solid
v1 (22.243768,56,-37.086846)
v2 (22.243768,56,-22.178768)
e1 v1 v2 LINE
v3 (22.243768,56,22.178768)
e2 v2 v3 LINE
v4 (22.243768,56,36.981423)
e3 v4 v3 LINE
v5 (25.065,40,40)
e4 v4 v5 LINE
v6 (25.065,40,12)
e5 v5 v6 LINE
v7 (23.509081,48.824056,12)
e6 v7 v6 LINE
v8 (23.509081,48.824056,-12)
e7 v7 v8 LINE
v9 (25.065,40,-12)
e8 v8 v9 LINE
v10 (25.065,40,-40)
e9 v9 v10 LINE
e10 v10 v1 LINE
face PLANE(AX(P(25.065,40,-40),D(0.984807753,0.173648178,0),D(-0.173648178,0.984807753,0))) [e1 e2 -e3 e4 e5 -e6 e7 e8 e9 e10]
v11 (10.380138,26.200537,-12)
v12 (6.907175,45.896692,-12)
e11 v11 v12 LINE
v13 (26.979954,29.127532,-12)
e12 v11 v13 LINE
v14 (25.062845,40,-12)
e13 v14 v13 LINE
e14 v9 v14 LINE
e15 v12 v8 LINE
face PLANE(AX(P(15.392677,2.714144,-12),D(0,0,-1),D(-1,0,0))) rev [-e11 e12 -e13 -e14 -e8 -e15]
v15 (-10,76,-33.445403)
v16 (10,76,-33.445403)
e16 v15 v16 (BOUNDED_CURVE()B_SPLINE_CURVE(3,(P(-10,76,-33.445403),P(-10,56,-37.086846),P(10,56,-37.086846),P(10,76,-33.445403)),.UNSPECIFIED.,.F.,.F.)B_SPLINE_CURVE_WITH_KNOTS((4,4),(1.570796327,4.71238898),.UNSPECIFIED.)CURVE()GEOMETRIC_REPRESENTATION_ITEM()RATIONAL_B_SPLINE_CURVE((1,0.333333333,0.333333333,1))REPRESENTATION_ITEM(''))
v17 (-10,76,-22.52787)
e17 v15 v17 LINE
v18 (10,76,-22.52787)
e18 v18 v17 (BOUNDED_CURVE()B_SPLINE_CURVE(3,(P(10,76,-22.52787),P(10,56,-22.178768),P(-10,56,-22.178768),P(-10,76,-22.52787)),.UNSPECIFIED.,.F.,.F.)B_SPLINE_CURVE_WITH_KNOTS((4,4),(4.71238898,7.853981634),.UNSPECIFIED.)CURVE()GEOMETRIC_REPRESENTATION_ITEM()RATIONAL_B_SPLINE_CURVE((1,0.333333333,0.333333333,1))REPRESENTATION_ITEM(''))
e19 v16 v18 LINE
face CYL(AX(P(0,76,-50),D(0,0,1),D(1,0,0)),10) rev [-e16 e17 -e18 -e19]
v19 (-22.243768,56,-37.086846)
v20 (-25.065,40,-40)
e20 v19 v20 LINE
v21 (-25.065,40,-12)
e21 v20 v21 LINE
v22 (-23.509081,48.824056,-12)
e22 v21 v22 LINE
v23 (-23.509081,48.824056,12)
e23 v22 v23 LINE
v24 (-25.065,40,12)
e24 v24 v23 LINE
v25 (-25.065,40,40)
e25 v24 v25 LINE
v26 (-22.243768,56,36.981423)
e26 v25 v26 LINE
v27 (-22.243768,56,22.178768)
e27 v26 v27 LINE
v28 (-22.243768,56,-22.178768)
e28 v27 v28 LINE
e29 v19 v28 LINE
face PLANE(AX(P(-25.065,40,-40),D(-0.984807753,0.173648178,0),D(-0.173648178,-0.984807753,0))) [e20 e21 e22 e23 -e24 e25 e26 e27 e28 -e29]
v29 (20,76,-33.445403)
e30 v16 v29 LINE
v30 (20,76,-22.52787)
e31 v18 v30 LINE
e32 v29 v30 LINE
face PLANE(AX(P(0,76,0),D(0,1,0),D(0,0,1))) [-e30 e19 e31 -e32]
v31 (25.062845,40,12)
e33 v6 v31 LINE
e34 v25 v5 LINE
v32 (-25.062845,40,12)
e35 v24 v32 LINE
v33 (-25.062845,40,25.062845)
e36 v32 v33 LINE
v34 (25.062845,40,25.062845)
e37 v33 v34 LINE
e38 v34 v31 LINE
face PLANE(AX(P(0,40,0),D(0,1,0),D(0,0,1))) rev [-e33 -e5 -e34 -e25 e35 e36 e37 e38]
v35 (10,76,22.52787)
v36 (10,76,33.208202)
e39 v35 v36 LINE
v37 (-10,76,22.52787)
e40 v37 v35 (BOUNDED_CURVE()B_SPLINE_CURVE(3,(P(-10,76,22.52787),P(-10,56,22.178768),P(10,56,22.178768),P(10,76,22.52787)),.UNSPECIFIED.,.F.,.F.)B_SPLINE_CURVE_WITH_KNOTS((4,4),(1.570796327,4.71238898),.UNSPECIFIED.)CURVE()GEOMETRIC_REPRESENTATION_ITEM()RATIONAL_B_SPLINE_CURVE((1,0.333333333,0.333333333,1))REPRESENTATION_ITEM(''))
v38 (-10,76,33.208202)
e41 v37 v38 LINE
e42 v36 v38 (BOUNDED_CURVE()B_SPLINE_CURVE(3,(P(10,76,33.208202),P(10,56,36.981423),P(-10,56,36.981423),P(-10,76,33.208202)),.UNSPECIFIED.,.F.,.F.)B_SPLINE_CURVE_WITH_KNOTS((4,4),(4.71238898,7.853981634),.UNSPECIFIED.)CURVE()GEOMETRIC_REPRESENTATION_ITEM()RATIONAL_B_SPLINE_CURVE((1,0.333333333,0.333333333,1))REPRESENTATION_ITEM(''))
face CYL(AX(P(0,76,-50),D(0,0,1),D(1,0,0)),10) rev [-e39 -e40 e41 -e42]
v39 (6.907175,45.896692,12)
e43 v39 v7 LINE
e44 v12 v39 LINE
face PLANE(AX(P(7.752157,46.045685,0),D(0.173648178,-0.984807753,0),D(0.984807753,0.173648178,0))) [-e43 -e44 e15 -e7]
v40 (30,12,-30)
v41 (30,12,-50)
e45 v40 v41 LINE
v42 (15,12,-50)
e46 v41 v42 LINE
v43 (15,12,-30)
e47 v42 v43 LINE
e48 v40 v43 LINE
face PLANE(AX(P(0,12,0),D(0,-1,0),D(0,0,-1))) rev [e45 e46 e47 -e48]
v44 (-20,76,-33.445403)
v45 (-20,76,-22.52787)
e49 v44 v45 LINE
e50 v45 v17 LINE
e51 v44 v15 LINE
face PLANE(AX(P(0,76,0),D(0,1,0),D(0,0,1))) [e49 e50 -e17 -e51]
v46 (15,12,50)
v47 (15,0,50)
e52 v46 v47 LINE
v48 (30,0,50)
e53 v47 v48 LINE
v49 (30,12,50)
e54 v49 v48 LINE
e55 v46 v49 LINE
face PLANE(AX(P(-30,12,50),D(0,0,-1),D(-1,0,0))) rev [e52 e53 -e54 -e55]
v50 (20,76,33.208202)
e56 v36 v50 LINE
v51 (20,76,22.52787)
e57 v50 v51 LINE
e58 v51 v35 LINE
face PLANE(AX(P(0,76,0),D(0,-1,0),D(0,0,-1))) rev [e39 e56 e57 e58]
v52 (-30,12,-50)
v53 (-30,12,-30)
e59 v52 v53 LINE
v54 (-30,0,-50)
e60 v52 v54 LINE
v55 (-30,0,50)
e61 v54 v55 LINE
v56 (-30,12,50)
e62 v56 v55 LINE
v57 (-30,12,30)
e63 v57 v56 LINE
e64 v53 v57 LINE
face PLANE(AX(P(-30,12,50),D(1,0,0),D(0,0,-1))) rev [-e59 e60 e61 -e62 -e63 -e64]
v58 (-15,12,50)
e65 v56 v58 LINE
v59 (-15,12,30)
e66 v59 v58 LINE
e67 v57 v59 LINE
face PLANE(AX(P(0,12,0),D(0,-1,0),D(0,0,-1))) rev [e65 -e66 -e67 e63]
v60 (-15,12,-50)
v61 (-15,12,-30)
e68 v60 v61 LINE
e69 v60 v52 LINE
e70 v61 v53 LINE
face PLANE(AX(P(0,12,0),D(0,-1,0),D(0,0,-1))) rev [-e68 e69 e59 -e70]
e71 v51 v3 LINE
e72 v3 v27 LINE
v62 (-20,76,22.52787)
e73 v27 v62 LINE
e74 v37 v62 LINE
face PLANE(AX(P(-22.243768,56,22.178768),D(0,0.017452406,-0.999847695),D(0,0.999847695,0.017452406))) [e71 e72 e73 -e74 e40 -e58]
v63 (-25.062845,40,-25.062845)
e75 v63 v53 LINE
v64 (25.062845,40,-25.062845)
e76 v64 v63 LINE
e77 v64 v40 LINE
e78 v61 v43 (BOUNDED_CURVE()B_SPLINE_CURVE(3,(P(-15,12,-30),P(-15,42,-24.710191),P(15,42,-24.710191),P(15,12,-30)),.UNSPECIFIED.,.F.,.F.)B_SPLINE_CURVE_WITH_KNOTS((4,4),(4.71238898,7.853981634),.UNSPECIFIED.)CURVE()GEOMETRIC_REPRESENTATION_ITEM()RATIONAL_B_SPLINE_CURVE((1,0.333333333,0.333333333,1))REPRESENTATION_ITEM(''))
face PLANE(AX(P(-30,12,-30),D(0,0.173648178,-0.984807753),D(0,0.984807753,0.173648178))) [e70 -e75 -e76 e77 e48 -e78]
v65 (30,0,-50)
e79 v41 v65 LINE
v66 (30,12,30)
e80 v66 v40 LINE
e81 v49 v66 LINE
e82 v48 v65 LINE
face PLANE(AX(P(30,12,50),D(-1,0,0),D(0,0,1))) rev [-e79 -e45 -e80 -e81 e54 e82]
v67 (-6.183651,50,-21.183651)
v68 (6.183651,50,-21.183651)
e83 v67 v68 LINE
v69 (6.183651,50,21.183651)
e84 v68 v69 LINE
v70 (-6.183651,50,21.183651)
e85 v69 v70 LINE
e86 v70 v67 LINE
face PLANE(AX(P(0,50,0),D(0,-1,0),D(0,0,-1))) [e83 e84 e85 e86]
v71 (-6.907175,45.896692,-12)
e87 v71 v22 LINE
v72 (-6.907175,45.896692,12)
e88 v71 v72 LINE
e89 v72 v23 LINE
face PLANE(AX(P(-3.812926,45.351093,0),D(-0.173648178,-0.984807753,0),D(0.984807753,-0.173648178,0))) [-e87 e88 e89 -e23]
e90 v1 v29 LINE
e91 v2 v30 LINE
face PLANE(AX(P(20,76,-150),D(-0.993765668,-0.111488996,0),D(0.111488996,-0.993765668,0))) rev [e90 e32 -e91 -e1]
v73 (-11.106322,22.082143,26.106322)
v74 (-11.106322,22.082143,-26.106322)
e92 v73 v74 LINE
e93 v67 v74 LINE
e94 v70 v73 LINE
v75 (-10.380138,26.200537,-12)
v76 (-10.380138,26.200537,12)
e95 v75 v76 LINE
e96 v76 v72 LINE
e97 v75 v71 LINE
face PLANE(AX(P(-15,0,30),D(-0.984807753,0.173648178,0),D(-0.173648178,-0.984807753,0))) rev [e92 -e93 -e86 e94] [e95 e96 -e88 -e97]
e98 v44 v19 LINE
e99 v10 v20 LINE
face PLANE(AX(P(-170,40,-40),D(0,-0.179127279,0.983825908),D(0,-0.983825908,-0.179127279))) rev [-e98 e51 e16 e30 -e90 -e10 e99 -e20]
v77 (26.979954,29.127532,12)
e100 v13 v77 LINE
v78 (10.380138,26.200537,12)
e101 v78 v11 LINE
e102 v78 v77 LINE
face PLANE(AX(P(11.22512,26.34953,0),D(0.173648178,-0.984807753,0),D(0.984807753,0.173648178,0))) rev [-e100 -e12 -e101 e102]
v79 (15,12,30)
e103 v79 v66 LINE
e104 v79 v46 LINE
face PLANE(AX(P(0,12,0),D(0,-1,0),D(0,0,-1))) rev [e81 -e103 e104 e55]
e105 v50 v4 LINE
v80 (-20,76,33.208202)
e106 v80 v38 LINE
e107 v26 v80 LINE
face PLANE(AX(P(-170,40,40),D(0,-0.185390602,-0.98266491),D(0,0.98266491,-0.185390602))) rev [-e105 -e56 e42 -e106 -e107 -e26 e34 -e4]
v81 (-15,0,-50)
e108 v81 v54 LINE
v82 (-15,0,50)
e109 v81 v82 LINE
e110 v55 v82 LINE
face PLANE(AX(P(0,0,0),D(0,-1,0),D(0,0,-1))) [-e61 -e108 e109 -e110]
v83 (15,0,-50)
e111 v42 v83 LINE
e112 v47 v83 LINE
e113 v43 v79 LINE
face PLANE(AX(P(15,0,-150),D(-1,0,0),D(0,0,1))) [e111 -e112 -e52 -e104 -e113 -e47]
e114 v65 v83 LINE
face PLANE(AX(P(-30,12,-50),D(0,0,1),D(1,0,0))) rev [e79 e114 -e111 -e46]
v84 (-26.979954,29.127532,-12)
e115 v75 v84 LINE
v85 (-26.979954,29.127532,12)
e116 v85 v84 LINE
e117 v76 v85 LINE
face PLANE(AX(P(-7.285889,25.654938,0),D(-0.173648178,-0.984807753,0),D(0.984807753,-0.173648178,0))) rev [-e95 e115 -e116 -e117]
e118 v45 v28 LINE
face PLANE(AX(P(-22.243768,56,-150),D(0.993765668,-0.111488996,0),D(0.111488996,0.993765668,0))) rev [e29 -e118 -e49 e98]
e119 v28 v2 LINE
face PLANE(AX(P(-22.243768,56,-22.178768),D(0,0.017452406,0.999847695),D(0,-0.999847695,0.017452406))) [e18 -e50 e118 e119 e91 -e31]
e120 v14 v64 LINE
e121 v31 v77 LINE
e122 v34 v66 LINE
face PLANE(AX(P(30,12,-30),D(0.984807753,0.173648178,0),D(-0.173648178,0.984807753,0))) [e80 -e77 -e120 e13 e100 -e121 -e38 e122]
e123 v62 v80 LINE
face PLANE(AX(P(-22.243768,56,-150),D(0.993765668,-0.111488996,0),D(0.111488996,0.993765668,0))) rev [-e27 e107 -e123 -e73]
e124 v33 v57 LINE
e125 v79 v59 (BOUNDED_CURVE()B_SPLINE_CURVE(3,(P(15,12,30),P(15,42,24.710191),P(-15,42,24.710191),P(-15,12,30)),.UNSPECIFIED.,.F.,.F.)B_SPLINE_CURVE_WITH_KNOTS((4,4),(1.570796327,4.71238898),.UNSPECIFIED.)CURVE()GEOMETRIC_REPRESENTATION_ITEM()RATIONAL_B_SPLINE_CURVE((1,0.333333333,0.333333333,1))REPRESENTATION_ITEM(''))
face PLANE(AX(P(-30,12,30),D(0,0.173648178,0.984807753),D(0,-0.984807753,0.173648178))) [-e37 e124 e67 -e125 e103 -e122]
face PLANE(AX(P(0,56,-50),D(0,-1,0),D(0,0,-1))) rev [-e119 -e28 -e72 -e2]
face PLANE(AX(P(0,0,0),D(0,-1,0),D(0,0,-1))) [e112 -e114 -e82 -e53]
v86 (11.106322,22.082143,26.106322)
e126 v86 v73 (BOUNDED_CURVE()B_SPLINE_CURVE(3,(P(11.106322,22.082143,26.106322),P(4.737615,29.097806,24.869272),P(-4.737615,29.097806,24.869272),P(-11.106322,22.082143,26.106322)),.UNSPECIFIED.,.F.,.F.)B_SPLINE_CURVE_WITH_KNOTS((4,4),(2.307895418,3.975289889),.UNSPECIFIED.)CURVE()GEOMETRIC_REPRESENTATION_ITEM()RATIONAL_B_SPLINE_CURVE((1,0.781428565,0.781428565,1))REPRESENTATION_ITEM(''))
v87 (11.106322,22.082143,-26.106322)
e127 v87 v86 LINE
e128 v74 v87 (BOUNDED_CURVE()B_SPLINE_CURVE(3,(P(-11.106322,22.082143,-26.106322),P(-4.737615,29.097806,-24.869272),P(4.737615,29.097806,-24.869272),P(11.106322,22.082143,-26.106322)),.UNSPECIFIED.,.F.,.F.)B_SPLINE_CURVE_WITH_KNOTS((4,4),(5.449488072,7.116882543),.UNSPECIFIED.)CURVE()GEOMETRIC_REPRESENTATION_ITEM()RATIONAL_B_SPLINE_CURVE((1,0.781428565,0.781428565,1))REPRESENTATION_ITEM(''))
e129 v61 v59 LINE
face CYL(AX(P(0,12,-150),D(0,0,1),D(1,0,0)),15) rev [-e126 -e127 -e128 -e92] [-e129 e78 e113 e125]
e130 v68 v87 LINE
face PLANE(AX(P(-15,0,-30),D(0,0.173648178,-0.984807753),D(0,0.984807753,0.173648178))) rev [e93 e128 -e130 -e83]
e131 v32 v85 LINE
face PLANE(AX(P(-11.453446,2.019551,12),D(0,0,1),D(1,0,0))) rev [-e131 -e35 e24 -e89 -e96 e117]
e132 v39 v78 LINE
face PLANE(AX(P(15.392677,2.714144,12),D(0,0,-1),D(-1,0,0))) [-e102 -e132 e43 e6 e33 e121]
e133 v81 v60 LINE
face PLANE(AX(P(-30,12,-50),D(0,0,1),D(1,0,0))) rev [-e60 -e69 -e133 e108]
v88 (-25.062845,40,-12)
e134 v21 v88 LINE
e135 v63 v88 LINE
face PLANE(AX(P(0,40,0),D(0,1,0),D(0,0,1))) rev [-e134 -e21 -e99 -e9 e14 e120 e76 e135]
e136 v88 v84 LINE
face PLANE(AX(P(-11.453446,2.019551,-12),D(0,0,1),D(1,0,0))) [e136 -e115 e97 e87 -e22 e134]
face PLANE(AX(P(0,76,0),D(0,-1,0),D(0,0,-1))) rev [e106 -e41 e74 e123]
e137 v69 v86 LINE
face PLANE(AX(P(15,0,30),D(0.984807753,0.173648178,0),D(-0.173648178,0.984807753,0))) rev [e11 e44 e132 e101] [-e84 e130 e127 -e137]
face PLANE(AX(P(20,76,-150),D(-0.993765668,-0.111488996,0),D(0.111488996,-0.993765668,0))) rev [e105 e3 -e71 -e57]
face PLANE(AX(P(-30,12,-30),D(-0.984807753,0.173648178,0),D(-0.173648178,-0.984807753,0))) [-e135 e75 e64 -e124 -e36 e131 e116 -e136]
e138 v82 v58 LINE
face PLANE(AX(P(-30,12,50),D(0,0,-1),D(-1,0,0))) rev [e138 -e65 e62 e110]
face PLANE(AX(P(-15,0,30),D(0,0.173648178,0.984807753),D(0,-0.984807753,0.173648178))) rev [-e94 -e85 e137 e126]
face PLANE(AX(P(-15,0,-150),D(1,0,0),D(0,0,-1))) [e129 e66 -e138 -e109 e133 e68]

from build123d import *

# Parameters (mm, degrees)
BASE_PLATE_SKETCH_W            = 60
BASE_PLATE_SKETCH_H            = 100
BASE_PLATE_100X60X12_DEPTH     = 12
PEDESTAL_SKETCH_W              = 60
PEDESTAL_SKETCH_H              = 60
TAPERED_PEDESTAL_DEPTH         = 28
TAPERED_PEDESTAL_TAPER         = 10
FOOT_CHANNEL_SKETCH_W          = 30
FOOT_CHANNEL_SKETCH_H          = 12
FOOT_CHANNEL_CUT_DEPTH         = 200
UPPER_BLOCK_SKETCH_W           = 50.13
UPPER_BLOCK_SKETCH_H           = 80
UPPER_BLOCK_80X50_DEPTH        = 16
UPPER_BLOCK_80X50_TAPER        = 10
TOP_SLOT_SKETCH_W              = 24
TOP_SLOT_SKETCH_H              = 8.960181453
TOP_SLOT_CUT_DEPTH             = 16
PEDESTAL_RELIEF_SKETCH_W       = 30
PEDESTAL_RELIEF_SKETCH_H       = 60
PEDESTAL_RELIEF_CUT_DEPTH      = 50
PEDESTAL_RELIEF_CUT_DRAFT      = -10
WINDOW_SKETCH_W                = 24
WINDOW_SKETCH_H                = 20
SQUARE_WINDOW_20X20_DEPTH      = 5
SIDE_POCKET_SKETCH_W           = 24
SIDE_POCKET_SKETCH_H           = 8.960181453
SIDE_POCKET_SKETCH_H_2         = 11.039818547
SIDE_POCKET_CUT_DEPTH          = 20
RIB_BOSS_SKETCH_W              = 44.487536618
RIB_BOSS_SKETCH_H              = 74.357536618
RIB_BOSS_DEPTH                 = 20
RIB_BOSS_TAPER                 = 10
TRIM_CUT_DEPTH                 = 100
UPRIGHTS_SKETCH_W              = 44.487536618
UPRIGHTS_SKETCH_H              = 15
UPRIGHTS_15X15_DEPTH           = 20
UPRIGHTS_15X15_DRAFT           = 1
UPRIGHTS_15X15_PROFILE_2_DEPTH = 20
UPRIGHTS_15X15_PROFILE_2_DRAFT = 1
CRADLE_CUT_A_DEPTH             = 200
CRADLE_CUT_B_DEPTH             = 200
CROSS_BORE_CUT_DEPTH           = 100


with BuildPart() as part:
    # Base Plate Sketch → Base Plate 100x60x12 (new body)
    with BuildSketch(Plane(origin=(0, 0, 0), x_dir=(1, 0, 0), z_dir=(0, 1, 0))):
        Rectangle(BASE_PLATE_SKETCH_W, BASE_PLATE_SKETCH_H)
    extrude(amount=BASE_PLATE_100X60X12_DEPTH)

    # Pedestal Sketch → Tapered Pedestal (add)
    with BuildSketch(Plane(origin=(0, 12, 0), x_dir=(1, 0, 0), z_dir=(0, 1, 0))):
        Rectangle(PEDESTAL_SKETCH_W, PEDESTAL_SKETCH_H)
    extrude(amount=TAPERED_PEDESTAL_DEPTH, taper=TAPERED_PEDESTAL_TAPER)

    # Foot Channel Sketch → Foot Channel Cut (cut)
    with BuildSketch(Plane.XY.offset(50)):
        with BuildLine():
            ThreePointArc((15, 12), (0, 27), (-15, 12))
            Line((-15, 12), (15, 12))
        make_face()
        with Locations((0, 6)):
            Rectangle(FOOT_CHANNEL_SKETCH_W, FOOT_CHANNEL_SKETCH_H)
    extrude(amount=-FOOT_CHANNEL_CUT_DEPTH, mode=Mode.SUBTRACT)

    # Upper Block Sketch → Upper Block 80x50 (add)
    with BuildSketch(Plane(origin=(0, 40, 0), x_dir=(1, 0, 0), z_dir=(0, 1, 0))):
        Rectangle(UPPER_BLOCK_SKETCH_W, UPPER_BLOCK_SKETCH_H)
    extrude(amount=UPPER_BLOCK_80X50_DEPTH, taper=UPPER_BLOCK_80X50_TAPER)

    # Top Slot Sketch → Top Slot Cut (cut)
    with BuildSketch(Plane(origin=(31.149600637, 5.492515031, 0), x_dir=(0, 0, -1), z_dir=(0.9848077530122081, 0.17364817766693072, 0))):
        with Locations((0, 39.519909274)):
            Rectangle(TOP_SLOT_SKETCH_W, TOP_SLOT_SKETCH_H)
        Polygon((-12, 35.039818547), (-12, 24), (0, 24), (12, 24), (12, 35.039818547), align=None)
    extrude(amount=-TOP_SLOT_CUT_DEPTH, mode=Mode.SUBTRACT)


with BuildPart() as pedestal_relief_cut_tool:
    # Pedestal Relief Sketch → Pedestal Relief Cut (with draft: the straight prism first)
    with BuildSketch(Plane.XZ):
        Rectangle(PEDESTAL_RELIEF_SKETCH_W, PEDESTAL_RELIEF_SKETCH_H)
    extrude(amount=-PEDESTAL_RELIEF_CUT_DEPTH)
    # Pedestal Relief Cut: the draft: its side faces are tilted about the plane it starts from
    pedestal_relief_cut_sides = [pedestal_relief_cut_tool.faces().sort_by_distance(p)[0] for p in [
        (-15, 25, 0),
        (0, 25, -30),
        (15, 25, 0),
        (0, 25, 30),
    ]]
    draft(pedestal_relief_cut_sides, Plane.XZ, PEDESTAL_RELIEF_CUT_DRAFT)


with BuildPart() as part_1:
    add(part.part)

    # Pedestal Relief Cut: cut by pedestal_relief_cut_tool
    add(pedestal_relief_cut_tool.part, mode=Mode.SUBTRACT)

    # Window Sketch → Square Window 20x20 (cut)
    with BuildSketch(Plane(origin=(15.392676588, 2.714144188, 0), x_dir=(0, 0, -1), z_dir=(0.9848077530122081, 0.1736481776669307, 0))):
        with Locations((0, 34)):
            Rectangle(WINDOW_SKETCH_W, WINDOW_SKETCH_H)
    extrude(amount=-SQUARE_WINDOW_20X20_DEPTH, mode=Mode.SUBTRACT)

    # Side Pocket Sketch → Side Pocket Cut (cut)
    with BuildSketch(Plane(origin=(-31.149600637, 5.492515031, 0), x_dir=(0, 0, 1), z_dir=(-0.9848077530122081, 0.17364817766693072, 0))):
        with Locations((0, 39.519909274)):
            Rectangle(SIDE_POCKET_SKETCH_W, SIDE_POCKET_SKETCH_H)
        with Locations((0, 29.519909274)):
            Rectangle(SIDE_POCKET_SKETCH_W, SIDE_POCKET_SKETCH_H_2)
    extrude(amount=-SIDE_POCKET_CUT_DEPTH, mode=Mode.SUBTRACT)

    # Rib Boss Sketch → Rib Boss (add)
    with BuildSketch(Plane(origin=(0, 56, 0), x_dir=(1, 0, 0), z_dir=(0, 1, 0))):
        Rectangle(RIB_BOSS_SKETCH_W, RIB_BOSS_SKETCH_H)
    extrude(amount=RIB_BOSS_DEPTH, taper=RIB_BOSS_TAPER)

    # Trim Sketch → Trim Cut (cut)
    with BuildSketch(Plane.XY.offset(50)):
        Polygon((0, 56), (24.962521637, 56), (24.962521637, 76), (-29.161824343, 76), (-29.161824343, 56), align=None)
    extrude(amount=-TRIM_CUT_DEPTH, mode=Mode.SUBTRACT)


with BuildPart() as uprights_15x15_tool:
    # Uprights Sketch → Uprights 15x15 (with draft: the straight prism first)
    with BuildSketch(Plane(origin=(0, 56, 0), x_dir=(1, 0, 0), z_dir=(0, 1, 0))):
        with Locations((0, 29.678768309)):
            Rectangle(UPRIGHTS_SKETCH_W, UPRIGHTS_SKETCH_H)
    extrude(amount=UPRIGHTS_15X15_DEPTH)
    # Uprights 15x15: the draft: its side faces are tilted about the plane it starts from
    uprights_15x15_sides = [uprights_15x15_tool.faces().sort_by_distance(p)[0] for p in [
        (-22.243768309, 66, -29.678768309),
        (0, 66, -22.178768309),
        (22.243768309, 66, -29.678768309),
        (0, 66, -37.178768309),
    ]]
    draft(uprights_15x15_sides, Plane(origin=(0, 56, 0), x_dir=(1, 0, 0), z_dir=(0, 1, 0)), UPRIGHTS_15X15_DRAFT)


with BuildPart() as part_2:
    add(part_1.part)

    # Uprights 15x15: add uprights_15x15_tool
    add(uprights_15x15_tool.part)


with BuildPart() as uprights_15x15_profile_2_tool:
    # Uprights Sketch → Uprights 15x15 profile 2 (with draft: the straight prism first)
    with BuildSketch(Plane(origin=(0, 56, 0), x_dir=(1, 0, 0), z_dir=(0, 1, 0))):
        with Locations((0, -29.678768309)):
            Rectangle(UPRIGHTS_SKETCH_W, UPRIGHTS_SKETCH_H)
    extrude(amount=UPRIGHTS_15X15_PROFILE_2_DEPTH)
    # Uprights 15x15 profile 2: the draft: its side faces are tilted about the plane it starts from
    uprights_15x15_profile_2_sides = [uprights_15x15_profile_2_tool.faces().sort_by_distance(p)[0] for p in [
        (0, 66, 37.178768309),
        (22.243768309, 66, 29.678768309),
        (0, 66, 22.178768309),
        (-22.243768309, 66, 29.678768309),
    ]]
    draft(uprights_15x15_profile_2_sides, Plane(origin=(0, 56, 0), x_dir=(1, 0, 0), z_dir=(0, 1, 0)), UPRIGHTS_15X15_PROFILE_2_DRAFT)


with BuildPart() as part_3:
    add(part_2.part)

    # Uprights 15x15 profile 2: add uprights_15x15_profile_2_tool
    add(uprights_15x15_profile_2_tool.part)

    # Cradle Cut A Sketch → Cradle Cut A (cut)
    with BuildSketch(Plane.XY.offset(50)):
        Polygon((20, 76), (22.243768309, 56), (21.89466701, 76), align=None)
        Polygon((-22.243768309, 56), (-20, 76), (-21.89466701, 76), align=None)
    extrude(amount=-CRADLE_CUT_A_DEPTH, mode=Mode.SUBTRACT)

    # Cradle Cut B Sketch → Cradle Cut B (cut)
    with BuildSketch(Plane(origin=(30, 0, 0), x_dir=(0, 0, -1), z_dir=(1, 0, 0))):
        Polygon((-40, 40), (-33.208201883, 76), (-36.82966701, 76), align=None)
        Polygon((40, 40), (33.445403325, 76), (36.82966701, 76), align=None)
    extrude(amount=-CRADLE_CUT_B_DEPTH, mode=Mode.SUBTRACT)

    # Cross Bore Sketch → Cross Bore Cut (cut)
    with BuildSketch(Plane.XY.offset(50)):
        with BuildLine():
            Line((-10, 76), (10, 76))
            ThreePointArc((10, 76), (0, 66), (-10, 76))
        make_face()
    extrude(amount=-CROSS_BORE_CUT_DEPTH, mode=Mode.SUBTRACT)


solid = part_3.part
